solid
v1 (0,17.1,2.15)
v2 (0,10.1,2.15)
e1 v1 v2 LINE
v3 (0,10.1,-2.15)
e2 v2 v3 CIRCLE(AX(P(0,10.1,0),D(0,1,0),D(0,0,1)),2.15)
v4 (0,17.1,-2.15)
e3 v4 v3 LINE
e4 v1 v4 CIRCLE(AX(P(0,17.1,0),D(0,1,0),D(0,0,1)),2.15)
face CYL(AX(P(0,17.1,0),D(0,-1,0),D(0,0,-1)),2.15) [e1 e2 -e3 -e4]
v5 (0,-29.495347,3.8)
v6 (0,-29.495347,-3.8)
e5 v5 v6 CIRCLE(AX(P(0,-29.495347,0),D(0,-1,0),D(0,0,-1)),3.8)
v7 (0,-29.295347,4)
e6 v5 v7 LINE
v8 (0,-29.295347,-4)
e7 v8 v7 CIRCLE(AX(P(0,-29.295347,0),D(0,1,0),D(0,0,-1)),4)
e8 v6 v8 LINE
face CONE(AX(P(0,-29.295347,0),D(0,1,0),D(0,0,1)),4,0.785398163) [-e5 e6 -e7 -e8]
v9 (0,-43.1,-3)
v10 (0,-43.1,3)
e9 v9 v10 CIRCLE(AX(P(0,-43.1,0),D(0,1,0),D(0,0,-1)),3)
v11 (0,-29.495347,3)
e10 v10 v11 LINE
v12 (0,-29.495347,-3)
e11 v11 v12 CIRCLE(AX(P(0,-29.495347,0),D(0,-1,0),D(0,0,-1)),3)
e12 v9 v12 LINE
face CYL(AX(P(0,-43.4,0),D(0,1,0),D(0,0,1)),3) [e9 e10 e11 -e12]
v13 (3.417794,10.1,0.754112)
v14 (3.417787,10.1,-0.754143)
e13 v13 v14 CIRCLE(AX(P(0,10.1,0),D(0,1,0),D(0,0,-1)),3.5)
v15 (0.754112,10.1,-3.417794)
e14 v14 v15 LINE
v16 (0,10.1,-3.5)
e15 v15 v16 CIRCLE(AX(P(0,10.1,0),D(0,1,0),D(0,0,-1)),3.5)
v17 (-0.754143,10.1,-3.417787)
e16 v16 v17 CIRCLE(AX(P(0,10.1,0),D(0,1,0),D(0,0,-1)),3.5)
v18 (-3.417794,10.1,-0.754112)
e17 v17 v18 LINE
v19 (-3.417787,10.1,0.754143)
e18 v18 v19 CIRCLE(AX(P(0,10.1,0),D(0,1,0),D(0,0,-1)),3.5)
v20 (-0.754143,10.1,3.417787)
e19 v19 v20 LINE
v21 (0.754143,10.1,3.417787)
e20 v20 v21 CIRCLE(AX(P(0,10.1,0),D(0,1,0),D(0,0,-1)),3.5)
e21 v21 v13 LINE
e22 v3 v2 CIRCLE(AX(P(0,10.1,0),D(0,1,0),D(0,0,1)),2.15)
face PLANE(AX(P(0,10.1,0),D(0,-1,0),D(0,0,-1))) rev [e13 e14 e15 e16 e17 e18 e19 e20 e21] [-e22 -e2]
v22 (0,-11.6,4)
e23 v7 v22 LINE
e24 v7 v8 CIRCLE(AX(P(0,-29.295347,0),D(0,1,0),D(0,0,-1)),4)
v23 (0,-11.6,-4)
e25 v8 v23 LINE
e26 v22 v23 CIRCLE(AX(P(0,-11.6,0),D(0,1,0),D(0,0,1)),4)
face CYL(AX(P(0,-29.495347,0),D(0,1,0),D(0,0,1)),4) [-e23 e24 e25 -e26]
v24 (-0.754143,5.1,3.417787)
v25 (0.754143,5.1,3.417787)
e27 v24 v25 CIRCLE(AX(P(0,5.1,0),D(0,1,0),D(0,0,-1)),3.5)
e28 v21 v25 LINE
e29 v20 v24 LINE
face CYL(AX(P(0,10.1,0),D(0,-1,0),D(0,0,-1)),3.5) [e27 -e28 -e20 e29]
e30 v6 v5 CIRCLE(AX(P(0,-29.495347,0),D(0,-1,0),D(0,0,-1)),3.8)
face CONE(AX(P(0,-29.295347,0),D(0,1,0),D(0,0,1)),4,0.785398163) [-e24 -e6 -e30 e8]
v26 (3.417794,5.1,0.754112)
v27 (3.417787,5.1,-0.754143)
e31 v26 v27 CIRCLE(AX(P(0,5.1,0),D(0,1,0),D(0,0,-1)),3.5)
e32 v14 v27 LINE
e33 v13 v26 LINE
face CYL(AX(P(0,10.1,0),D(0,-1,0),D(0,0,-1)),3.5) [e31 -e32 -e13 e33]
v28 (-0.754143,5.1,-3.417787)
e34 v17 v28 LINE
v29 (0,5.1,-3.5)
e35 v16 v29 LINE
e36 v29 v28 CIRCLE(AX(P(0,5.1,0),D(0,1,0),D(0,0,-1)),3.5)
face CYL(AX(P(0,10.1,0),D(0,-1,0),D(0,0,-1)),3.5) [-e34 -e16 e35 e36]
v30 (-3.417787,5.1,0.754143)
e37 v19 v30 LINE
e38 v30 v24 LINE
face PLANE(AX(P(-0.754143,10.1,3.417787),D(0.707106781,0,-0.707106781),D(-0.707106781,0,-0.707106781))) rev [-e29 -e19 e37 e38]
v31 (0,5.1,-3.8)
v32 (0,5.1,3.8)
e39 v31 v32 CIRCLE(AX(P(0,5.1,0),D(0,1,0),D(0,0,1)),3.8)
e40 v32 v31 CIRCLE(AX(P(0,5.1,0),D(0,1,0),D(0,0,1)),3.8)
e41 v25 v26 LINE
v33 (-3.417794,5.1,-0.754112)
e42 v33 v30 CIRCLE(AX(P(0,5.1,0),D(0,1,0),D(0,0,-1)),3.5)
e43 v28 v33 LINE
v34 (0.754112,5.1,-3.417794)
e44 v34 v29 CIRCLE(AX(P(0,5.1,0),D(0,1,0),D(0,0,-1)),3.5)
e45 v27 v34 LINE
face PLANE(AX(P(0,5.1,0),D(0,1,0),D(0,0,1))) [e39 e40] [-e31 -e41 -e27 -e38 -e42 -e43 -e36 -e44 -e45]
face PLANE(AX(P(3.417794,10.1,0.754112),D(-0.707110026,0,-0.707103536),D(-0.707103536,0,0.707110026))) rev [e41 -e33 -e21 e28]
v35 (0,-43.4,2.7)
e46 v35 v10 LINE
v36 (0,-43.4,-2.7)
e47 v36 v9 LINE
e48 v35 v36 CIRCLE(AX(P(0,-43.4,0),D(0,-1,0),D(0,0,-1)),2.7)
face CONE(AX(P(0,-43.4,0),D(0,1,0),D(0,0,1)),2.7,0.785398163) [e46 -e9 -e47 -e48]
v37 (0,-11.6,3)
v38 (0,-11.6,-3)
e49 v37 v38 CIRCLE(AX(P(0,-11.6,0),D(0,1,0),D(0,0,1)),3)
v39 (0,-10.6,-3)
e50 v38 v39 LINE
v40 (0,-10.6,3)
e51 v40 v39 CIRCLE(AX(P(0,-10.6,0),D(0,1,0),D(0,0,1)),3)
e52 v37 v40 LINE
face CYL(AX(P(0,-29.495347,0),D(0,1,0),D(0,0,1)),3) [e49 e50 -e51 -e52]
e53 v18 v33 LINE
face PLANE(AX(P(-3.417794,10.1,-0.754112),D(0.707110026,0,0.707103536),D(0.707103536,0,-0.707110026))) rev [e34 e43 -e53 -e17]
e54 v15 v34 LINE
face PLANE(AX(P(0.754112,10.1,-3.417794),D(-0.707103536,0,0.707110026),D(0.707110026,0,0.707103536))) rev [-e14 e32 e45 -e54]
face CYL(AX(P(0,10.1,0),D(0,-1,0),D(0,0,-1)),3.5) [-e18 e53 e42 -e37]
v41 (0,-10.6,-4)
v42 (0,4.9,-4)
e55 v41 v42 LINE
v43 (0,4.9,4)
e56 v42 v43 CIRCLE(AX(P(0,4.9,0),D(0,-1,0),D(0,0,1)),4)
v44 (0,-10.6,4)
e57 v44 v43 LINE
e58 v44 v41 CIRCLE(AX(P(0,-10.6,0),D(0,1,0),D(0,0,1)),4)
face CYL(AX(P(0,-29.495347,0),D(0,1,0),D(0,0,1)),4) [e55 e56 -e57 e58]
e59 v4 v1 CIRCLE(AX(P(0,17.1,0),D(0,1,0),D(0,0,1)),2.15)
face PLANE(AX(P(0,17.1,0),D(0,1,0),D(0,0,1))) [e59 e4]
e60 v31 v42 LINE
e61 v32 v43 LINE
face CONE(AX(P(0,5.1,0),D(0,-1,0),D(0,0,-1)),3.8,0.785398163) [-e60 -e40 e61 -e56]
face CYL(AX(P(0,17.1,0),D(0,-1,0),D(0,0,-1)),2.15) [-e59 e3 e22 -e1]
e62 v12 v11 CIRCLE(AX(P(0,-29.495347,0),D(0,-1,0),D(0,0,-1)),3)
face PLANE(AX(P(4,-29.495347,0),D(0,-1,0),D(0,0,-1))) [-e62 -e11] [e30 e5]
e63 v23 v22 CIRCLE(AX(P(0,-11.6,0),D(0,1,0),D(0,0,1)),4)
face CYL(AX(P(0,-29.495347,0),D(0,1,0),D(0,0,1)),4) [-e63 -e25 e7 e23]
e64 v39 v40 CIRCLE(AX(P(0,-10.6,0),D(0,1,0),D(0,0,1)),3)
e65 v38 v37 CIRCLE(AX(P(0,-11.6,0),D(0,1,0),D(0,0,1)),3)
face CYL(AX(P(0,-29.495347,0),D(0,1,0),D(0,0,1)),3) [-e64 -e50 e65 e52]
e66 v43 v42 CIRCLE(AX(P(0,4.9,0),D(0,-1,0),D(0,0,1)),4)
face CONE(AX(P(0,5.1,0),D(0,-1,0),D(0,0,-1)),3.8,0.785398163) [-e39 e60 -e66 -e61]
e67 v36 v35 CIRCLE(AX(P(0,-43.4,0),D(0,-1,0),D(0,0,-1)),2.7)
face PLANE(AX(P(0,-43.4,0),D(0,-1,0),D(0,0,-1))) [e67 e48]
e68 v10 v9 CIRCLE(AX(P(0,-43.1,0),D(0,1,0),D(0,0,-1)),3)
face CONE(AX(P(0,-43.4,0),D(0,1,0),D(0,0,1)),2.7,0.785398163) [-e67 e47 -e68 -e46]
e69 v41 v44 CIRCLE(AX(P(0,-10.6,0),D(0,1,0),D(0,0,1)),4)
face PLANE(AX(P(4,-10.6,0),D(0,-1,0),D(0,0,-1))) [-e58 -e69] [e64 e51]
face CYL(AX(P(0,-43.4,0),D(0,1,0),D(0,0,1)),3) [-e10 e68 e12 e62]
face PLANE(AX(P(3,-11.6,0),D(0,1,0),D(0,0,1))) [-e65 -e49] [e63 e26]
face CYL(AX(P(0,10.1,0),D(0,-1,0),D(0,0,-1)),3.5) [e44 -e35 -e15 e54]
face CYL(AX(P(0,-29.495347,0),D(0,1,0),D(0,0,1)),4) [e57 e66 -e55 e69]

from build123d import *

# Parameters (mm, degrees)
BOSS_EXTRUDE1_START = 13.904652831
SKETCH2_R           = 3
BOSS_EXTRUDE1_DEPTH = 13.904652831
BOSS_EXTRUDE2_DEPTH = 5
SKETCH4_R           = 2.15
BOSS_EXTRUDE3_DEPTH = 7
CHAMFER1_SIZE       = 0.2
CHAMFER2_SIZE       = 0.3


with BuildPart() as part:
    # Sketch1 → Revolve1 (revolve)
    with BuildSketch(Plane(origin=(0, 0, 0), x_dir=(-1, 0, 0), z_dir=(0, 0, -1)), mode=Mode.PRIVATE) as revolve1_sk:
        Polygon((-4, -29.495347169), (0, -29.495347169), (0, 5.1), (-4, 5.1), (-4, -10.6), (-3, -10.6), (-3, -11.6), (-4, -11.6), align=None)
    revolve(revolve1_sk.sketch.rotate(Axis((0, -29.495347169, 0), (0, 1, 0)), 270), axis=Axis((0, -29.495347169, 0), (0, 1, 0)))

    # Sketch2 → Boss-Extrude1 (add)
    with BuildSketch(Plane.XZ.offset(29.495347169).offset(BOSS_EXTRUDE1_START)):
        with Locations(Location((0, 0, 0), (0, 0, 90))):
            Circle(SKETCH2_R)
    extrude(amount=-BOSS_EXTRUDE1_DEPTH)

    # Sketch3 → Boss-Extrude2 (add)
    with BuildSketch(Plane(origin=(0, 5.1, 0), x_dir=(-1, 0, 0), z_dir=(0, 1, 0))):
        with BuildLine():
            Line((3.417793986, -0.754111574), (0.754142944, -3.417787065))
            ThreePointArc((0.754142944, -3.417787065), (1.6062e-05, -3.5), (-0.754111574, -3.417793986))
            Line((-0.754111574, -3.417793986), (-3.417787065, -0.754142944))
            ThreePointArc((-3.417787065, -0.754142944), (-3.5, -1.6062e-05), (-3.417793986, 0.754111574))
            Line((-3.417793986, 0.754111574), (-0.754142944, 3.417787065))
            ThreePointArc((-0.754142944, 3.417787065), (0, 3.5), (0.754142944, 3.417787065))
            Line((0.754142944, 3.417787065), (3.417787065, 0.754142944))
            ThreePointArc((3.417787065, 0.754142944), (3.5, 1.6062e-05), (3.417793986, -0.754111574))
        make_face()
    extrude(amount=BOSS_EXTRUDE2_DEPTH)

    # Sketch4 → Boss-Extrude3 (add)
    with BuildSketch(Plane(origin=(0, 10.1, 0), x_dir=(-1, 0, 0), z_dir=(0, 1, 0))):
        with Locations(Location((0, 0, 0), (0, 0, 90))):
            Circle(SKETCH4_R)
    extrude(amount=BOSS_EXTRUDE3_DEPTH)

    # Chamfer1
    chamfer1_edges = [part.edges().sort_by_distance(p)[0] for p in [
        (0, -29.495347169, -4),
        (0, 5.1, -4),
    ]]
    chamfer(chamfer1_edges, length=CHAMFER1_SIZE)

    # Chamfer2
    chamfer2_edges = [part.edges().sort_by_distance(p)[0] for p in [
        (0, -43.4, -3),
    ]]
    chamfer(chamfer2_edges, length=CHAMFER2_SIZE)


solid = part.part
